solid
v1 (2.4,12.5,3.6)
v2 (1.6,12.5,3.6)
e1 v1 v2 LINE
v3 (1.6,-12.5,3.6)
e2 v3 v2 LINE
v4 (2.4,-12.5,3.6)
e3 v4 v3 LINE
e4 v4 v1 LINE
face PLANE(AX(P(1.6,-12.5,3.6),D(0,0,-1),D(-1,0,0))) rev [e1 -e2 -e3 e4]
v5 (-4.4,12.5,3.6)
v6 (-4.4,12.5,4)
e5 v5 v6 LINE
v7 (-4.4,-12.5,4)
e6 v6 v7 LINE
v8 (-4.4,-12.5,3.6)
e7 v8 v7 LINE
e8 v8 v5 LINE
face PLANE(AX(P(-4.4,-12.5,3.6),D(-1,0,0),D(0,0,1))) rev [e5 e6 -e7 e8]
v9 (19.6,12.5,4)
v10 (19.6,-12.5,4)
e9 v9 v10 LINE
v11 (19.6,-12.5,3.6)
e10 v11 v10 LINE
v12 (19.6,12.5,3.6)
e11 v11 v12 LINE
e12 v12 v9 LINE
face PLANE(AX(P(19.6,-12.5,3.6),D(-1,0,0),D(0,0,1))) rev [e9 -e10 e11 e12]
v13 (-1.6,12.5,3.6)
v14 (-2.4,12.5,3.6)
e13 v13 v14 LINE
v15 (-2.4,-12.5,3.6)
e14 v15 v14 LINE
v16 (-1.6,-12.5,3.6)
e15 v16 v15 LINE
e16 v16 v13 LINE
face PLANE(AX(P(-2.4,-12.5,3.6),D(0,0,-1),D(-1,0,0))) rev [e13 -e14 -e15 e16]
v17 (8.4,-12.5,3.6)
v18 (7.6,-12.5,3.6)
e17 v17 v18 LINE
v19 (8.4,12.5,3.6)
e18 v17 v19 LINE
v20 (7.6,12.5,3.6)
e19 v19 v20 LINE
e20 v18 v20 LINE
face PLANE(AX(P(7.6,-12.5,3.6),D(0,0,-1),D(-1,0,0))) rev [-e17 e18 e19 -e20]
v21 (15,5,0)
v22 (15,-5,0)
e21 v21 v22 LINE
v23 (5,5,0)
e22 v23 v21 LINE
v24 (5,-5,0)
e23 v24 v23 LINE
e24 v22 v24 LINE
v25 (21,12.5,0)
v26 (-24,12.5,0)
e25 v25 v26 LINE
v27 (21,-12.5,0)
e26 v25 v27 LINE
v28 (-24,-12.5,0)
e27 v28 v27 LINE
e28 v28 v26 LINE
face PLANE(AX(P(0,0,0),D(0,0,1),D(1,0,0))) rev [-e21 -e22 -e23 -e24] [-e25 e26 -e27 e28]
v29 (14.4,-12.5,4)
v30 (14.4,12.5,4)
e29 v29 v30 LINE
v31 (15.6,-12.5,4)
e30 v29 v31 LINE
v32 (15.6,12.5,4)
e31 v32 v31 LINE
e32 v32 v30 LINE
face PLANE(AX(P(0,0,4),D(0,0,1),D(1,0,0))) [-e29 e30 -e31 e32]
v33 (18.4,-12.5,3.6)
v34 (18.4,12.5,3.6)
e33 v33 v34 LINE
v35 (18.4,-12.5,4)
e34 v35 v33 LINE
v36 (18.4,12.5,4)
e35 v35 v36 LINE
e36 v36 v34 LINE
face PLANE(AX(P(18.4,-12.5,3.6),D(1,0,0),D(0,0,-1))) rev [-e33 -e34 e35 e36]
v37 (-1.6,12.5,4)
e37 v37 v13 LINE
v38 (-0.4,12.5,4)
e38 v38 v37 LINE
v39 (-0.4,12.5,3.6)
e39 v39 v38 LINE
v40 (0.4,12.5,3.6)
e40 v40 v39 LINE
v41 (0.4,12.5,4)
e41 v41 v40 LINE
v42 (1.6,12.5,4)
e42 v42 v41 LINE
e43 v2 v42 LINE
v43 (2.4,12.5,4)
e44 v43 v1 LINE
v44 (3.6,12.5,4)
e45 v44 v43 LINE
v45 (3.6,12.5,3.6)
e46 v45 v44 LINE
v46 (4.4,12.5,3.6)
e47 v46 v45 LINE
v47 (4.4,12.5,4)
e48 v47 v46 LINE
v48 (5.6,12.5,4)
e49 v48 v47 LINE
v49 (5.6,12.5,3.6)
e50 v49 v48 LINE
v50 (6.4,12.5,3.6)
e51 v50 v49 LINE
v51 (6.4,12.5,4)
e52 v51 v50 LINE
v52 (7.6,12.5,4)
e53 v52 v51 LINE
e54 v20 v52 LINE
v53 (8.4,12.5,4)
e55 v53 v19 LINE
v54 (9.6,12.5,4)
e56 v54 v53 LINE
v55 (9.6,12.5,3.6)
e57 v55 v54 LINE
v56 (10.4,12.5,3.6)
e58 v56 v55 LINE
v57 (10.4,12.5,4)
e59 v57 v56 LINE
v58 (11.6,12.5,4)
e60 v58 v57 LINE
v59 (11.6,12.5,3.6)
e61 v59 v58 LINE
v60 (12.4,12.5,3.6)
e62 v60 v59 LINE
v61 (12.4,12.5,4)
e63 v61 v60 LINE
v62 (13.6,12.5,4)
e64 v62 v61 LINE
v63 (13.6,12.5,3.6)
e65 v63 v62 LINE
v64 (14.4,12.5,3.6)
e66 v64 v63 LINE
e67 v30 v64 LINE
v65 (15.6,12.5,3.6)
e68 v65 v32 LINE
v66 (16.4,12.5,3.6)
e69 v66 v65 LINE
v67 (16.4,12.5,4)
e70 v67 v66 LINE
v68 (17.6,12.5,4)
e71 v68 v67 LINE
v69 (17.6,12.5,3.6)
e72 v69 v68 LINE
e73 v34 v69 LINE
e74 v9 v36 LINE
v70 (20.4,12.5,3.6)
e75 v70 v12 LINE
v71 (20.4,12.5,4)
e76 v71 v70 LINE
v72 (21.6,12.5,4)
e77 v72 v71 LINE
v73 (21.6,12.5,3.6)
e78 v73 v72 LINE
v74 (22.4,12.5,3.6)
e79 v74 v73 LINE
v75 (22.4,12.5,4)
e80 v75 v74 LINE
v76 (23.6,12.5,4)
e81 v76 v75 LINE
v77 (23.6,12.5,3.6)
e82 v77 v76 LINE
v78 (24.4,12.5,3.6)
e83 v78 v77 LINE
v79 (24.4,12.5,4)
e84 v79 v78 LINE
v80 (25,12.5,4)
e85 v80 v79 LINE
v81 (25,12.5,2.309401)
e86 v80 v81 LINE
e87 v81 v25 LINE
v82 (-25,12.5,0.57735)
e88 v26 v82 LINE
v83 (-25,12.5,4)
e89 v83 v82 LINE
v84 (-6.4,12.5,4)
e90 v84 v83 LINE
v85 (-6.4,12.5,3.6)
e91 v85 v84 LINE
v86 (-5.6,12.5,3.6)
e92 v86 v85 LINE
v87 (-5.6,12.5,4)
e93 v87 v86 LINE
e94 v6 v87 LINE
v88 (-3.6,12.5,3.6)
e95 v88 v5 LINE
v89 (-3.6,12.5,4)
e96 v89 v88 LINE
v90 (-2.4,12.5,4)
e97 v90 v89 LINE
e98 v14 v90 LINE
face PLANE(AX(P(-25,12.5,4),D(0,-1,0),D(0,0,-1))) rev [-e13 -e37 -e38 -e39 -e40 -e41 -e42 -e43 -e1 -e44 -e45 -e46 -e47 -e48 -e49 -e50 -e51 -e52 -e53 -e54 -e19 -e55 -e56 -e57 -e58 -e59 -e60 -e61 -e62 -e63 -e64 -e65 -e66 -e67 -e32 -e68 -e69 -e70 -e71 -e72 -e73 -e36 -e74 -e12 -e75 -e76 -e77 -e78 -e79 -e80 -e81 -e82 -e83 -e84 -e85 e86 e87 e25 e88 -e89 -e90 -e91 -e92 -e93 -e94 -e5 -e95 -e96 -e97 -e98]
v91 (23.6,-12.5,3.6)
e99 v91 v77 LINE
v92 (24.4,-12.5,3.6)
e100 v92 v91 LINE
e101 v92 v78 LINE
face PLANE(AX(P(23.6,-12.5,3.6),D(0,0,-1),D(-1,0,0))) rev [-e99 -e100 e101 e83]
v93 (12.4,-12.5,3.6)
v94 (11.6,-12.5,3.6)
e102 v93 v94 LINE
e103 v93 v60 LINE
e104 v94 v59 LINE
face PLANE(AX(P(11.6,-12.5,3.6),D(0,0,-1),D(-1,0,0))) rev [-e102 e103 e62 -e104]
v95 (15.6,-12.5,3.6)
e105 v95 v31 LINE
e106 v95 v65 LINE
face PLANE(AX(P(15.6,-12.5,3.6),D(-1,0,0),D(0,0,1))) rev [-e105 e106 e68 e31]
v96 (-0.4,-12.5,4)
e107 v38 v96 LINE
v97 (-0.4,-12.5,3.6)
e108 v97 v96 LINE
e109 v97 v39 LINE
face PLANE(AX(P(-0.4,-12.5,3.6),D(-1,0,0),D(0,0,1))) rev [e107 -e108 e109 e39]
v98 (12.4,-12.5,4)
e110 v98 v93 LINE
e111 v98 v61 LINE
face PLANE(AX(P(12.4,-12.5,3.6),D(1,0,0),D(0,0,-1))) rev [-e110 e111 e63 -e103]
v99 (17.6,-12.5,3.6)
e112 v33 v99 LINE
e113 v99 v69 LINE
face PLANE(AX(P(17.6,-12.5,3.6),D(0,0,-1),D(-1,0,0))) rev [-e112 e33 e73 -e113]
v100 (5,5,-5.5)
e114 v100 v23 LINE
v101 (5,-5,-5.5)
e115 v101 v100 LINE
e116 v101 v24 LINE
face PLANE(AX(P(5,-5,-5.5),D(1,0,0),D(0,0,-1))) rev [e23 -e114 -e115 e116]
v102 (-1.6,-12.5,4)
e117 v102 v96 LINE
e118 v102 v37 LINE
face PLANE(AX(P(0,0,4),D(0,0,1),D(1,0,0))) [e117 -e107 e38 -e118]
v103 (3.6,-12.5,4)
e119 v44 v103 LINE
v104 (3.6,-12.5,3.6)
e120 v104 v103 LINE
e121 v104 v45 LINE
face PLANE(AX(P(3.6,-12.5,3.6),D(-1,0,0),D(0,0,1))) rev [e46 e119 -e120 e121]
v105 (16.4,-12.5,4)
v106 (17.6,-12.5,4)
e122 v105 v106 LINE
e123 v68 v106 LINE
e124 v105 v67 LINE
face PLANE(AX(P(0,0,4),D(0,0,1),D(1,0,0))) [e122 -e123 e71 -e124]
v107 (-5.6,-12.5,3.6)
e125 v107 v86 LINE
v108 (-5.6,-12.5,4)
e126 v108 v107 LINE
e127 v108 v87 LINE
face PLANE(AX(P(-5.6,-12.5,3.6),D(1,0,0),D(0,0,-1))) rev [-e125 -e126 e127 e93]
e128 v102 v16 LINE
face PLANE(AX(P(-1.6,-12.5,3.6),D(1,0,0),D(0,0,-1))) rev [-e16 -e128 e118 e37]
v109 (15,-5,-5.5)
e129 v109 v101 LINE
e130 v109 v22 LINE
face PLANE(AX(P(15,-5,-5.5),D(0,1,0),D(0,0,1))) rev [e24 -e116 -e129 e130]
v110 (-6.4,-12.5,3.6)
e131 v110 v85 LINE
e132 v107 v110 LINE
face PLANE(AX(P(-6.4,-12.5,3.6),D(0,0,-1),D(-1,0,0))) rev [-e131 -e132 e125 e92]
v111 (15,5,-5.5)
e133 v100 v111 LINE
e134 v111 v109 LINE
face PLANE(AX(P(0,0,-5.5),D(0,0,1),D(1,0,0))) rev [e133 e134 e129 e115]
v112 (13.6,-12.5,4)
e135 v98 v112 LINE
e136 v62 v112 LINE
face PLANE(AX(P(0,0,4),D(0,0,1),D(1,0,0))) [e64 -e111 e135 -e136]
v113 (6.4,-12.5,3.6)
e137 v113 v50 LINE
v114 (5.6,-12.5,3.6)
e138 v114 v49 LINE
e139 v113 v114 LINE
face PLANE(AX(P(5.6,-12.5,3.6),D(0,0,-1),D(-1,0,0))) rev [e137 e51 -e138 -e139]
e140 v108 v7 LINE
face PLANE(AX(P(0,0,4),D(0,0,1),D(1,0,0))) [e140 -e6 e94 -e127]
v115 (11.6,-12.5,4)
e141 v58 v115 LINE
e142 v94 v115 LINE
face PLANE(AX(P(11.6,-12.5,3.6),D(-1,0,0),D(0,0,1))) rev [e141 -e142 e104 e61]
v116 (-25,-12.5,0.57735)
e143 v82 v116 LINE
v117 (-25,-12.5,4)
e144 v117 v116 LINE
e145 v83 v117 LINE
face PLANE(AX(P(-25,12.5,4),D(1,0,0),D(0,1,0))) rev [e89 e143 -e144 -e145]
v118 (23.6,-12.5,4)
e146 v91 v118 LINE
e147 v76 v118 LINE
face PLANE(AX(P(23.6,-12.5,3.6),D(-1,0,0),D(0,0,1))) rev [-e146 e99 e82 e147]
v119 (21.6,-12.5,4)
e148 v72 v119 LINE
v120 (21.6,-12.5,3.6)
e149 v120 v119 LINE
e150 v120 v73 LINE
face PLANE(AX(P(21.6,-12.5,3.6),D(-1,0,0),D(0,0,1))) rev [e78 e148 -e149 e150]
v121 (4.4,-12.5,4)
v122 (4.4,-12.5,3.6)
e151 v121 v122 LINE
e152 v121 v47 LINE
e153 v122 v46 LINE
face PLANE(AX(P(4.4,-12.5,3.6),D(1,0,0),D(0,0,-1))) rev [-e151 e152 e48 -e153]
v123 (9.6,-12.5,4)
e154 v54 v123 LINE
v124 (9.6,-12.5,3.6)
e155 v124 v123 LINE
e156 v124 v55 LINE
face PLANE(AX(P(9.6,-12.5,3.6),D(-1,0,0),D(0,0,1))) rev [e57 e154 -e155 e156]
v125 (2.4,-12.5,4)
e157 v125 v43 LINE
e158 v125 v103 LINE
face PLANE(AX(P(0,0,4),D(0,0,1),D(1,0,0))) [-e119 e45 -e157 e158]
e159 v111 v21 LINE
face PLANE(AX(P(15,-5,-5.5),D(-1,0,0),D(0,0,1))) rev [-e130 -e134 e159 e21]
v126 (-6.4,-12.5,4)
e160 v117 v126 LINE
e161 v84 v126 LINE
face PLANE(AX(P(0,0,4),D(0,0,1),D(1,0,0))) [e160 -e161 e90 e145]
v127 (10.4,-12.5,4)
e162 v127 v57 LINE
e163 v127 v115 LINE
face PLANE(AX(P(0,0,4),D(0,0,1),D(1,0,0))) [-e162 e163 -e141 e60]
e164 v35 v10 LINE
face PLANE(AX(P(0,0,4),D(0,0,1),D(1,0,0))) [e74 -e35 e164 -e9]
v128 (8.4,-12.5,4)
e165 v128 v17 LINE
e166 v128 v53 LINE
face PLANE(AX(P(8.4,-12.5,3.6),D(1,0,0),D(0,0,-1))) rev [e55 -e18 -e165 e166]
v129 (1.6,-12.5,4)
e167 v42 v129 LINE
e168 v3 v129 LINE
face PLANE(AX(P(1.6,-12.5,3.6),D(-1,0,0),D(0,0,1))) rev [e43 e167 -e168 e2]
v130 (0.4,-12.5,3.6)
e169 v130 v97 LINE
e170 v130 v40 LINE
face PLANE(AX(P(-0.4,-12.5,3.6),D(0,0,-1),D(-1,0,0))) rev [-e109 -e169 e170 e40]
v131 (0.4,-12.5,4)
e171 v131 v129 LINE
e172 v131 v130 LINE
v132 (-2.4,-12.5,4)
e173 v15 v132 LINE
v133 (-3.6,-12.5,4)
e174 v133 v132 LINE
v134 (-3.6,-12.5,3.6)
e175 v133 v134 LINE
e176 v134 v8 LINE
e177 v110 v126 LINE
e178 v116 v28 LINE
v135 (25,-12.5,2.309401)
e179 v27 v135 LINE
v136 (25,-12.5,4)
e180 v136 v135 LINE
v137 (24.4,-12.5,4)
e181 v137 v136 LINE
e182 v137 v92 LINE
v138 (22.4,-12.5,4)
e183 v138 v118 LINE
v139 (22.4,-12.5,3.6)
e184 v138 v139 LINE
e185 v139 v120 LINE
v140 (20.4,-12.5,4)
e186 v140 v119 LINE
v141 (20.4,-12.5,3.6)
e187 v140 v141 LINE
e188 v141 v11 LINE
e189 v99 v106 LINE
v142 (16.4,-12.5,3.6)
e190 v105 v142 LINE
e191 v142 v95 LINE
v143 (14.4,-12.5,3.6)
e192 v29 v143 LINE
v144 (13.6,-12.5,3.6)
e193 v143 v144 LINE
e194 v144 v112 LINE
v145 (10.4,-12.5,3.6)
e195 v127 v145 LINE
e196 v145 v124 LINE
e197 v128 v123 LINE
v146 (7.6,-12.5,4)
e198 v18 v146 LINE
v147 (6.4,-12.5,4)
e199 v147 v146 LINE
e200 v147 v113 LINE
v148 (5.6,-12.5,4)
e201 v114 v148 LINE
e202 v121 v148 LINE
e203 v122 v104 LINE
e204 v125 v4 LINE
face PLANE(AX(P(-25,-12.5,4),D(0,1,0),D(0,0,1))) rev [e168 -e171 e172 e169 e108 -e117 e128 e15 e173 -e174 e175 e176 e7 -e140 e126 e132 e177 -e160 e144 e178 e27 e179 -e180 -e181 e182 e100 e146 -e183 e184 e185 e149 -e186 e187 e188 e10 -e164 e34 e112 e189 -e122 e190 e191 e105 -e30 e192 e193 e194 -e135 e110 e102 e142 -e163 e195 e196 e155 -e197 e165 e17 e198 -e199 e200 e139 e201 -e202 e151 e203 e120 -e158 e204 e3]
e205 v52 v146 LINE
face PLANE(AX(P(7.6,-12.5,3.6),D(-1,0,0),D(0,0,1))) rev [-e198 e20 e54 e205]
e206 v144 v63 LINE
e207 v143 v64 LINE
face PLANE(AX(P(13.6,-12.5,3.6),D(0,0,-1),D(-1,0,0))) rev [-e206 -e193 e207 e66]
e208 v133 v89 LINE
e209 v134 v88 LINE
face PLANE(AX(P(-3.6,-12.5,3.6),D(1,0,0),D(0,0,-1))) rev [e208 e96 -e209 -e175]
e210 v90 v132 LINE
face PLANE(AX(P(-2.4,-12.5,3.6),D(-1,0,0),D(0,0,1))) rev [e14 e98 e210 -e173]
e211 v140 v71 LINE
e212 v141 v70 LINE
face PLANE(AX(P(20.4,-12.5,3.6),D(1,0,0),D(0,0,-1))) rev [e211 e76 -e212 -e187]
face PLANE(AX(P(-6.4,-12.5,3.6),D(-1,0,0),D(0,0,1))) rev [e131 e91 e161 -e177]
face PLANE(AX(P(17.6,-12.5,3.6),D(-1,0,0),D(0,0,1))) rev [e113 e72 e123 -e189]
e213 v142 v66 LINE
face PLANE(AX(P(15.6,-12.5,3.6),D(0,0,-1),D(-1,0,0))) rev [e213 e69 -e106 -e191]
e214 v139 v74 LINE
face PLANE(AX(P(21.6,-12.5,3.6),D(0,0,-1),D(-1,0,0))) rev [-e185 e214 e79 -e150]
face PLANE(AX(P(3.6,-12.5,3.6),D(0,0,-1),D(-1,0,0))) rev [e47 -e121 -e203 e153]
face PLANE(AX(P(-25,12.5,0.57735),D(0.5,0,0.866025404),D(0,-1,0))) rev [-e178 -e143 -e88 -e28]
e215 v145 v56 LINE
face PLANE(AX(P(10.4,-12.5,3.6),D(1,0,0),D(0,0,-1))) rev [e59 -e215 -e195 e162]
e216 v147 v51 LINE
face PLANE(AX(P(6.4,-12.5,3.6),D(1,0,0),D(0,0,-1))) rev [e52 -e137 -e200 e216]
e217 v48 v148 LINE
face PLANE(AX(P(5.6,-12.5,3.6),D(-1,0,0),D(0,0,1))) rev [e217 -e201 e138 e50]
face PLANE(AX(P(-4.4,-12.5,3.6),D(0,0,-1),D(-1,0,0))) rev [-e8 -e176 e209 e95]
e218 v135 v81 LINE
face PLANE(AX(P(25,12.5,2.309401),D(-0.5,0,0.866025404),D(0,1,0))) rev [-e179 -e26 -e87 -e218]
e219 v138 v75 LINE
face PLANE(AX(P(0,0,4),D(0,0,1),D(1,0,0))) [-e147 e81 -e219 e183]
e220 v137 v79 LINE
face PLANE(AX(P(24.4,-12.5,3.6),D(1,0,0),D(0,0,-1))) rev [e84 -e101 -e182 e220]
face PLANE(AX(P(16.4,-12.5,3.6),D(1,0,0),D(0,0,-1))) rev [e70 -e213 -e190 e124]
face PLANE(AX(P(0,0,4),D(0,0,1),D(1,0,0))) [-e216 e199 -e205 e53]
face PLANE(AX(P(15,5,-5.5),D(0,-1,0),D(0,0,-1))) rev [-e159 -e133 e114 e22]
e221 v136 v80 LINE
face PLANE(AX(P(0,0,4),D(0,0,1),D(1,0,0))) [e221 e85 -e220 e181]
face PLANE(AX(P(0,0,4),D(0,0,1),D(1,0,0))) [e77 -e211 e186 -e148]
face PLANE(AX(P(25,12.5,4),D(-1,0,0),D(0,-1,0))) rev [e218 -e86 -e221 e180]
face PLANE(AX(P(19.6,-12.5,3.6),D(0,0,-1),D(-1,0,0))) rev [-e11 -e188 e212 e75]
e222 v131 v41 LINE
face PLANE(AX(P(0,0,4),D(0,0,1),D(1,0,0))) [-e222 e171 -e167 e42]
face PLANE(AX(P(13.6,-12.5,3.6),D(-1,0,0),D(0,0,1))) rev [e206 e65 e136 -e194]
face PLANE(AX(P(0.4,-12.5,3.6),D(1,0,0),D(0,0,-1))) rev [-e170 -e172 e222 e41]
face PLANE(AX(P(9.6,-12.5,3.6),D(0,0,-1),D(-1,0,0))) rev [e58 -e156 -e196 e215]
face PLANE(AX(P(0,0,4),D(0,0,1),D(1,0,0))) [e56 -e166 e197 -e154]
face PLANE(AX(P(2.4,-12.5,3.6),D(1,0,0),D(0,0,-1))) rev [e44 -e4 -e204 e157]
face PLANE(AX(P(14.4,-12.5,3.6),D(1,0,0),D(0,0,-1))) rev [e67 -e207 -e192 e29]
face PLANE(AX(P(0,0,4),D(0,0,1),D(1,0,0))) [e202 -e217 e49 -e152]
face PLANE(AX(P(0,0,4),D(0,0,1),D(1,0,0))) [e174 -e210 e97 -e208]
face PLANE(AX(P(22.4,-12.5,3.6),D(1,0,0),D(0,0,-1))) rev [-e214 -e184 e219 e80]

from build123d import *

# Parameters (mm, degrees)
SKETCH1_W           = 50
SKETCH1_H           = 25
BOSS_EXTRUDE1_DEPTH = 4
CHAMFER1_SIZE       = 4
CHAMFER1_SIZE2      = 2.309401077
SKETCH2_W           = 10
SKETCH2_H           = 10
BOSS_EXTRUDE2_DEPTH = 5.5
SKETCH3_W           = 0.8
SKETCH3_H           = 0.8
CUT_EXTRUDE1_DEPTH  = 36.780581326
LPATTERN1_COUNT     = 16
LPATTERN1_PITCH     = 2
CHAMFER2_SIZE       = 1
CHAMFER2_SIZE2      = 0.577350269


with BuildPart() as part:
    # Sketch1 → Boss-Extrude1 (new body)
    with BuildSketch(Plane.XY):
        Rectangle(SKETCH1_W, SKETCH1_H)
    extrude(amount=BOSS_EXTRUDE1_DEPTH)

    # Chamfer1
    chamfer1_edges = [part.edges().sort_by_distance(p)[0] for p in [
        (25, 0, 0),
    ]]
    chamfer1_side = [part.faces().sort_by_distance(p)[0] for p in [
        (0, 0, 0),
    ]]
    chamfer(chamfer1_edges, length=CHAMFER1_SIZE, length2=CHAMFER1_SIZE2, reference=chamfer1_side[0])

    # Sketch2 → Boss-Extrude2 (add)
    with BuildSketch(Plane(origin=(0, 0, 0), x_dir=(-1, 0, 0), z_dir=(0, 0, -1))):
        with Locations((-10, 0)):
            Rectangle(SKETCH2_W, SKETCH2_H)
    extrude(amount=BOSS_EXTRUDE2_DEPTH)

    # Sketch3 → Cut-Extrude1 (cut, through all)
    with BuildSketch(Plane(origin=(0, 12.5, 0), x_dir=(1, 0, 0), z_dir=(0, 1, 0))):
        with Locations((24, -4)):
            Rectangle(SKETCH3_W, SKETCH3_H)
    cut_extrude1 = extrude(amount=-CUT_EXTRUDE1_DEPTH, mode=Mode.SUBTRACT)

    # LPattern1: Cut-Extrude1 ×16
    with Locations(*[(-i * LPATTERN1_PITCH, 0, 0) for i in range(1, LPATTERN1_COUNT)]):
        add(cut_extrude1, mode=Mode.SUBTRACT)

    # Chamfer2
    chamfer2_edges = [part.edges().sort_by_distance(p)[0] for p in [
        (-25, 0, 0),
    ]]
    chamfer2_side = [part.faces().sort_by_distance(p)[0] for p in [
        (-3.142857143, 0, 0),
    ]]
    chamfer(chamfer2_edges, length=CHAMFER2_SIZE, length2=CHAMFER2_SIZE2, reference=chamfer2_side[0])


solid = part.part
